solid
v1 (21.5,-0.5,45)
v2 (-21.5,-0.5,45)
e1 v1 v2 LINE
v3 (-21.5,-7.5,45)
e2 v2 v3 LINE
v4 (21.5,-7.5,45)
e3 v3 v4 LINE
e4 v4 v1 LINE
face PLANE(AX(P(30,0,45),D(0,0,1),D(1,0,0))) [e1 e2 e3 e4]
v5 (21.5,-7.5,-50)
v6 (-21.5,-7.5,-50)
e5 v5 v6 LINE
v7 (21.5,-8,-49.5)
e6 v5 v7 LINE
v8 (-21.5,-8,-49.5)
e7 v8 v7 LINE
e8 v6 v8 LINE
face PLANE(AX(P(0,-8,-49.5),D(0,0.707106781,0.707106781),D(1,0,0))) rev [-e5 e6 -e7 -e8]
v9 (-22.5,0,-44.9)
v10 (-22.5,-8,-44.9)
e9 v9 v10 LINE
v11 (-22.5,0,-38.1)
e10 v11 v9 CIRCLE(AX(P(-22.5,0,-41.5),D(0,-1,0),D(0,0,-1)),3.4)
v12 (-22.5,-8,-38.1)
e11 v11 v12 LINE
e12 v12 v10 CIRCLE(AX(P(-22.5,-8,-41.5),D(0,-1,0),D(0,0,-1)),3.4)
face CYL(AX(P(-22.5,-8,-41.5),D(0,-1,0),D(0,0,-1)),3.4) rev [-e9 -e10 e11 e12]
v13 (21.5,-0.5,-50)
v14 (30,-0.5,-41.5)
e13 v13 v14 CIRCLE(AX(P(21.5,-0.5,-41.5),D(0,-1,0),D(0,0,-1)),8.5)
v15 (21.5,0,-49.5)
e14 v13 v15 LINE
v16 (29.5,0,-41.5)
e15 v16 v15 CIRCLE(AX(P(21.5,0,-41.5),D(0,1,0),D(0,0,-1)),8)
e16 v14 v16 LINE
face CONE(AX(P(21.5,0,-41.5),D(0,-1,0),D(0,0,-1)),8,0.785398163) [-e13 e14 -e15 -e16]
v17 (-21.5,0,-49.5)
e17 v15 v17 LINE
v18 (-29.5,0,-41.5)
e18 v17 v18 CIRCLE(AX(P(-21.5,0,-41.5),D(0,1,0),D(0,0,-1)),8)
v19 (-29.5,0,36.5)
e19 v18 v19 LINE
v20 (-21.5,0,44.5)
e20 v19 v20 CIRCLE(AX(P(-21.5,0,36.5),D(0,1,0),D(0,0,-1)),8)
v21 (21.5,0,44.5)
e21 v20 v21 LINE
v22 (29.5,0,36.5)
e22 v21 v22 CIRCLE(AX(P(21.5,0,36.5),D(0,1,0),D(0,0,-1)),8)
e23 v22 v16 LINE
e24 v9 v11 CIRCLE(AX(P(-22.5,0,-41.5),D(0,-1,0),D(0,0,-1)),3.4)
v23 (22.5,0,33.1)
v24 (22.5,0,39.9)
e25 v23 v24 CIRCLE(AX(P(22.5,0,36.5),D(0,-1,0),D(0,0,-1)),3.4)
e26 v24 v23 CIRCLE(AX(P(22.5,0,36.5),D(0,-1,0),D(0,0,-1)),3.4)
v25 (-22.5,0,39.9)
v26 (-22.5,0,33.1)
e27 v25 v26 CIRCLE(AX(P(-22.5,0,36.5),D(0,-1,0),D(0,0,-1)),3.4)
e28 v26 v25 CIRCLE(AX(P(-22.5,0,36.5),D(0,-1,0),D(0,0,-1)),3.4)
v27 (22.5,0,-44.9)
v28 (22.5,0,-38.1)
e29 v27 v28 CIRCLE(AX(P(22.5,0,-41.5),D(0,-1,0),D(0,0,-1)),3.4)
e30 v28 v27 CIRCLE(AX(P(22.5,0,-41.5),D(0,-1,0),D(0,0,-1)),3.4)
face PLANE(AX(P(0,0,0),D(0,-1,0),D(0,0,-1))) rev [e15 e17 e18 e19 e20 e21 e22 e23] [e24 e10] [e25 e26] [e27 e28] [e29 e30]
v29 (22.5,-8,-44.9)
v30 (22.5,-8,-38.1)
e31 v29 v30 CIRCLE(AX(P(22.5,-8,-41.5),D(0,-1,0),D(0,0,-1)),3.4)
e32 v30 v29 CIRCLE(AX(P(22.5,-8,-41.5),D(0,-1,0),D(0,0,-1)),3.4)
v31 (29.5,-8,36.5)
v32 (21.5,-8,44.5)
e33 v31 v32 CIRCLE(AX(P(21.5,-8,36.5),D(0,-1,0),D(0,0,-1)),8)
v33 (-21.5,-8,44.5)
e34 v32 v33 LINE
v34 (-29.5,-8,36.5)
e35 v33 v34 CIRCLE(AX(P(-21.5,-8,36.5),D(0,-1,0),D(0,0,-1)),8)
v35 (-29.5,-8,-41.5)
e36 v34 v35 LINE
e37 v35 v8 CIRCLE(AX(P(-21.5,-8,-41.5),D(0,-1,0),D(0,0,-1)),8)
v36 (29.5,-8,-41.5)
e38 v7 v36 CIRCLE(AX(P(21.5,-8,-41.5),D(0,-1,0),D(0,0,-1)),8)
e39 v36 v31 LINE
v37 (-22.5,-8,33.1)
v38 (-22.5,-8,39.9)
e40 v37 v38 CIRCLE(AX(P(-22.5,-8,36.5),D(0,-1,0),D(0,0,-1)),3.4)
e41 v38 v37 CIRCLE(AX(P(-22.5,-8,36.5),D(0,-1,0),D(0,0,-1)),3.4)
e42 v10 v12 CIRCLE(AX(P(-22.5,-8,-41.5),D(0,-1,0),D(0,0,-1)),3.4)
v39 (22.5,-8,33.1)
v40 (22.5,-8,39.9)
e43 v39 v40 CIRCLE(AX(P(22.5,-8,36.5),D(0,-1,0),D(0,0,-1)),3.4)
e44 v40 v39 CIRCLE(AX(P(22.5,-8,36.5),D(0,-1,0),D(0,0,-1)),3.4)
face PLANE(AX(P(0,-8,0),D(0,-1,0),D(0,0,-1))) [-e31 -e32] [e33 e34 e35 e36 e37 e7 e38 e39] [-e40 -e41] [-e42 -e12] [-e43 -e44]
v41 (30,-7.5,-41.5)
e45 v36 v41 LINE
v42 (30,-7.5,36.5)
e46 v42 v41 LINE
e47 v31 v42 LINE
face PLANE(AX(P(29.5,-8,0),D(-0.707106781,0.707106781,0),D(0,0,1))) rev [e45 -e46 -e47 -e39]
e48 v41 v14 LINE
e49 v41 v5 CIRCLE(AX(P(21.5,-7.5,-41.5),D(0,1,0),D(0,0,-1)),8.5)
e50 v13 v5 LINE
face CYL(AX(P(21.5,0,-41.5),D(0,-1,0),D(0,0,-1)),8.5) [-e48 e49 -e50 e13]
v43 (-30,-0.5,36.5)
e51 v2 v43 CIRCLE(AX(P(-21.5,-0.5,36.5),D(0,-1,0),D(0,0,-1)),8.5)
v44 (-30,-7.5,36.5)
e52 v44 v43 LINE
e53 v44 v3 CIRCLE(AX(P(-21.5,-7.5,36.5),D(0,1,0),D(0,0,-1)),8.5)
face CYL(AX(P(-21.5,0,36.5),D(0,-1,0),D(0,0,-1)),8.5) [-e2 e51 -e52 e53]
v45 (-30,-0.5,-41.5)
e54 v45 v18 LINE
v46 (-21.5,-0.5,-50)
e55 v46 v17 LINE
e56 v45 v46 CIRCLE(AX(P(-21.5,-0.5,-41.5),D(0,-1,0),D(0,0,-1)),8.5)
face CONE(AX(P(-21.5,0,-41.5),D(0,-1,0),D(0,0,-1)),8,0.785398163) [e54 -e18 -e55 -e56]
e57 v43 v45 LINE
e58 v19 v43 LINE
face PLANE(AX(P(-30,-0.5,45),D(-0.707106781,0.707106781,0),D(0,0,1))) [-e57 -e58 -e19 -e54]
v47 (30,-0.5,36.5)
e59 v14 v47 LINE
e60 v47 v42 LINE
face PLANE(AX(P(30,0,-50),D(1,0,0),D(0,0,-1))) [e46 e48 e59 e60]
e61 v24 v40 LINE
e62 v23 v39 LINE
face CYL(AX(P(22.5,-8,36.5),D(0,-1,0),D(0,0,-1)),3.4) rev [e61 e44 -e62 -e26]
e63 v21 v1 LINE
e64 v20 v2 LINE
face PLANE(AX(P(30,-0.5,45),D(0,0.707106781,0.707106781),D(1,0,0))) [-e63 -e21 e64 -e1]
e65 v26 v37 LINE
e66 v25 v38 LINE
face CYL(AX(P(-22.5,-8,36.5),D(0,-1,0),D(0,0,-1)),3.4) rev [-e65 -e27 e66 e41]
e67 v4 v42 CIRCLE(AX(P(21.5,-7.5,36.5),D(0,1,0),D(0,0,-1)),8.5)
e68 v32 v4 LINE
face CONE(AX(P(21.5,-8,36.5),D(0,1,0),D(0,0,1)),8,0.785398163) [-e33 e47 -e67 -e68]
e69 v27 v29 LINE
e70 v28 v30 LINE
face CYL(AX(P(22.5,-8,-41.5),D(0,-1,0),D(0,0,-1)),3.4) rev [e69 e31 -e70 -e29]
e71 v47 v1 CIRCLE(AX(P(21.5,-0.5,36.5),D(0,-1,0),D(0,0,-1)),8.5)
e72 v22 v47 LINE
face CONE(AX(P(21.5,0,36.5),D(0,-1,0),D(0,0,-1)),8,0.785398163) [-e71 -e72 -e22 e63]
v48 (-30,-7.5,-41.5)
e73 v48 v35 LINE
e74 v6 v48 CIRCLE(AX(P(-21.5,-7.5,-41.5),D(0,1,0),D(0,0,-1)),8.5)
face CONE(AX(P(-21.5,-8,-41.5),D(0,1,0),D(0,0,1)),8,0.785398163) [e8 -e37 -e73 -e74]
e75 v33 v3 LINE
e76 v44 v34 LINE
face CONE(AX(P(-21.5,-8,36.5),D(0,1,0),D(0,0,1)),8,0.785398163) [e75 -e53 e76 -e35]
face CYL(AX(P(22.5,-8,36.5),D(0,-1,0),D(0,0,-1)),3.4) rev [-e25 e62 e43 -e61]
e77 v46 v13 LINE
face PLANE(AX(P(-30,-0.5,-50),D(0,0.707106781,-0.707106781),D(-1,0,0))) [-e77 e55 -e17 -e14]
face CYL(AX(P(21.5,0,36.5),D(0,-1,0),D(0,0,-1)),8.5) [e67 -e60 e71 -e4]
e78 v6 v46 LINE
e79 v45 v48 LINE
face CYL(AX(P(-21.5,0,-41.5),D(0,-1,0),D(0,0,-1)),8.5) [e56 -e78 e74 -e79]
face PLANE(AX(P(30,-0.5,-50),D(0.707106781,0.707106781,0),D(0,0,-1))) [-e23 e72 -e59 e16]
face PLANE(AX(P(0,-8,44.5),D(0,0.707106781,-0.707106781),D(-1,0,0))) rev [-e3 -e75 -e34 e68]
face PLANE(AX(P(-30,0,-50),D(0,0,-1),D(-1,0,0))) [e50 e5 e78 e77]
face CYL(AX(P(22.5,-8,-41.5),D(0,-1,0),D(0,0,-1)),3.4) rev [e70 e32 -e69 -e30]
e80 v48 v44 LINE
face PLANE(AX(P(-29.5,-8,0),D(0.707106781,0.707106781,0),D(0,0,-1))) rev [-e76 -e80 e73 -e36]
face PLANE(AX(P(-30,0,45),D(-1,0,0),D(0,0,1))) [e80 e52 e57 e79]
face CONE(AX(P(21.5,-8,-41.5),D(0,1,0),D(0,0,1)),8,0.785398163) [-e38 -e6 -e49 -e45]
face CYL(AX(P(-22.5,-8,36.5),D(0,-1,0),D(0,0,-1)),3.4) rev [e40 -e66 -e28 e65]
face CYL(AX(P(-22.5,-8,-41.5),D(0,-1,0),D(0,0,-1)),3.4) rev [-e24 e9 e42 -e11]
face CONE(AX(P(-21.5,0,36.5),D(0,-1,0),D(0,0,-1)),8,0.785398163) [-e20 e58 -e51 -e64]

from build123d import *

# Parameters (mm, degrees)
SKETCH1_W                  = 60
SKETCH1_H                  = 95
BOSS_EXTRUDE1_DEPTH        = 8
F_6_8_6_8_DIAMETER_HOLE1_D = 6.8
FILLET1_R                  = 8.5
CHAMFER1_SIZE              = 0.5


with BuildPart() as part:
    # Sketch1 → Boss-Extrude1 (new body)
    with BuildSketch(Plane.XZ.offset(8)):
        with Locations((0, -2.5)):
            Rectangle(SKETCH1_W, SKETCH1_H)
    extrude(amount=-BOSS_EXTRUDE1_DEPTH)

    # Ø6.8 (6.8) Diameter Hole1 (through all)
    with Locations(Plane(origin=(0, -8, 0), x_dir=(-1, 0, 0), z_dir=(0, -1, 0))):
        with Locations((22.5, 41.5), (-22.5, 41.5), (-22.5, -36.5), (22.5, -36.5)):
            Hole(F_6_8_6_8_DIAMETER_HOLE1_D / 2)

    # Fillet1
    fillet1_edges = [part.edges().sort_by_distance(p)[0] for p in [
        (-30, -4, 45),
        (30, -4, 45),
        (30, -4, -50),
        (-30, -4, -50),
    ]]
    fillet(fillet1_edges, radius=FILLET1_R)

    # Chamfer1
    chamfer1_edges = [part.edges().sort_by_distance(p)[0] for p in [
        (0, -8, -50),
        (0, 0, -50),
        (-30, -8, -2.5),
        (30, -8, -2.5),
        (0, -8, 45),
        (-27.51040764, -8, 42.51040764),
        (-27.51040764, -8, -47.51040764),
        (27.51040764, -8, 42.51040764),
        (27.51040764, -8, -47.51040764),
        (30, 0, -2.5),
        (-30, 0, -2.5),
        (0, 0, 45),
        (-27.51040764, 0, 42.51040764),
        (-27.51040764, 0, -47.51040764),
        (27.51040764, 0, 42.51040764),
        (27.51040764, 0, -47.51040764),
    ]]
    chamfer(chamfer1_edges, length=CHAMFER1_SIZE)


solid = part.part
